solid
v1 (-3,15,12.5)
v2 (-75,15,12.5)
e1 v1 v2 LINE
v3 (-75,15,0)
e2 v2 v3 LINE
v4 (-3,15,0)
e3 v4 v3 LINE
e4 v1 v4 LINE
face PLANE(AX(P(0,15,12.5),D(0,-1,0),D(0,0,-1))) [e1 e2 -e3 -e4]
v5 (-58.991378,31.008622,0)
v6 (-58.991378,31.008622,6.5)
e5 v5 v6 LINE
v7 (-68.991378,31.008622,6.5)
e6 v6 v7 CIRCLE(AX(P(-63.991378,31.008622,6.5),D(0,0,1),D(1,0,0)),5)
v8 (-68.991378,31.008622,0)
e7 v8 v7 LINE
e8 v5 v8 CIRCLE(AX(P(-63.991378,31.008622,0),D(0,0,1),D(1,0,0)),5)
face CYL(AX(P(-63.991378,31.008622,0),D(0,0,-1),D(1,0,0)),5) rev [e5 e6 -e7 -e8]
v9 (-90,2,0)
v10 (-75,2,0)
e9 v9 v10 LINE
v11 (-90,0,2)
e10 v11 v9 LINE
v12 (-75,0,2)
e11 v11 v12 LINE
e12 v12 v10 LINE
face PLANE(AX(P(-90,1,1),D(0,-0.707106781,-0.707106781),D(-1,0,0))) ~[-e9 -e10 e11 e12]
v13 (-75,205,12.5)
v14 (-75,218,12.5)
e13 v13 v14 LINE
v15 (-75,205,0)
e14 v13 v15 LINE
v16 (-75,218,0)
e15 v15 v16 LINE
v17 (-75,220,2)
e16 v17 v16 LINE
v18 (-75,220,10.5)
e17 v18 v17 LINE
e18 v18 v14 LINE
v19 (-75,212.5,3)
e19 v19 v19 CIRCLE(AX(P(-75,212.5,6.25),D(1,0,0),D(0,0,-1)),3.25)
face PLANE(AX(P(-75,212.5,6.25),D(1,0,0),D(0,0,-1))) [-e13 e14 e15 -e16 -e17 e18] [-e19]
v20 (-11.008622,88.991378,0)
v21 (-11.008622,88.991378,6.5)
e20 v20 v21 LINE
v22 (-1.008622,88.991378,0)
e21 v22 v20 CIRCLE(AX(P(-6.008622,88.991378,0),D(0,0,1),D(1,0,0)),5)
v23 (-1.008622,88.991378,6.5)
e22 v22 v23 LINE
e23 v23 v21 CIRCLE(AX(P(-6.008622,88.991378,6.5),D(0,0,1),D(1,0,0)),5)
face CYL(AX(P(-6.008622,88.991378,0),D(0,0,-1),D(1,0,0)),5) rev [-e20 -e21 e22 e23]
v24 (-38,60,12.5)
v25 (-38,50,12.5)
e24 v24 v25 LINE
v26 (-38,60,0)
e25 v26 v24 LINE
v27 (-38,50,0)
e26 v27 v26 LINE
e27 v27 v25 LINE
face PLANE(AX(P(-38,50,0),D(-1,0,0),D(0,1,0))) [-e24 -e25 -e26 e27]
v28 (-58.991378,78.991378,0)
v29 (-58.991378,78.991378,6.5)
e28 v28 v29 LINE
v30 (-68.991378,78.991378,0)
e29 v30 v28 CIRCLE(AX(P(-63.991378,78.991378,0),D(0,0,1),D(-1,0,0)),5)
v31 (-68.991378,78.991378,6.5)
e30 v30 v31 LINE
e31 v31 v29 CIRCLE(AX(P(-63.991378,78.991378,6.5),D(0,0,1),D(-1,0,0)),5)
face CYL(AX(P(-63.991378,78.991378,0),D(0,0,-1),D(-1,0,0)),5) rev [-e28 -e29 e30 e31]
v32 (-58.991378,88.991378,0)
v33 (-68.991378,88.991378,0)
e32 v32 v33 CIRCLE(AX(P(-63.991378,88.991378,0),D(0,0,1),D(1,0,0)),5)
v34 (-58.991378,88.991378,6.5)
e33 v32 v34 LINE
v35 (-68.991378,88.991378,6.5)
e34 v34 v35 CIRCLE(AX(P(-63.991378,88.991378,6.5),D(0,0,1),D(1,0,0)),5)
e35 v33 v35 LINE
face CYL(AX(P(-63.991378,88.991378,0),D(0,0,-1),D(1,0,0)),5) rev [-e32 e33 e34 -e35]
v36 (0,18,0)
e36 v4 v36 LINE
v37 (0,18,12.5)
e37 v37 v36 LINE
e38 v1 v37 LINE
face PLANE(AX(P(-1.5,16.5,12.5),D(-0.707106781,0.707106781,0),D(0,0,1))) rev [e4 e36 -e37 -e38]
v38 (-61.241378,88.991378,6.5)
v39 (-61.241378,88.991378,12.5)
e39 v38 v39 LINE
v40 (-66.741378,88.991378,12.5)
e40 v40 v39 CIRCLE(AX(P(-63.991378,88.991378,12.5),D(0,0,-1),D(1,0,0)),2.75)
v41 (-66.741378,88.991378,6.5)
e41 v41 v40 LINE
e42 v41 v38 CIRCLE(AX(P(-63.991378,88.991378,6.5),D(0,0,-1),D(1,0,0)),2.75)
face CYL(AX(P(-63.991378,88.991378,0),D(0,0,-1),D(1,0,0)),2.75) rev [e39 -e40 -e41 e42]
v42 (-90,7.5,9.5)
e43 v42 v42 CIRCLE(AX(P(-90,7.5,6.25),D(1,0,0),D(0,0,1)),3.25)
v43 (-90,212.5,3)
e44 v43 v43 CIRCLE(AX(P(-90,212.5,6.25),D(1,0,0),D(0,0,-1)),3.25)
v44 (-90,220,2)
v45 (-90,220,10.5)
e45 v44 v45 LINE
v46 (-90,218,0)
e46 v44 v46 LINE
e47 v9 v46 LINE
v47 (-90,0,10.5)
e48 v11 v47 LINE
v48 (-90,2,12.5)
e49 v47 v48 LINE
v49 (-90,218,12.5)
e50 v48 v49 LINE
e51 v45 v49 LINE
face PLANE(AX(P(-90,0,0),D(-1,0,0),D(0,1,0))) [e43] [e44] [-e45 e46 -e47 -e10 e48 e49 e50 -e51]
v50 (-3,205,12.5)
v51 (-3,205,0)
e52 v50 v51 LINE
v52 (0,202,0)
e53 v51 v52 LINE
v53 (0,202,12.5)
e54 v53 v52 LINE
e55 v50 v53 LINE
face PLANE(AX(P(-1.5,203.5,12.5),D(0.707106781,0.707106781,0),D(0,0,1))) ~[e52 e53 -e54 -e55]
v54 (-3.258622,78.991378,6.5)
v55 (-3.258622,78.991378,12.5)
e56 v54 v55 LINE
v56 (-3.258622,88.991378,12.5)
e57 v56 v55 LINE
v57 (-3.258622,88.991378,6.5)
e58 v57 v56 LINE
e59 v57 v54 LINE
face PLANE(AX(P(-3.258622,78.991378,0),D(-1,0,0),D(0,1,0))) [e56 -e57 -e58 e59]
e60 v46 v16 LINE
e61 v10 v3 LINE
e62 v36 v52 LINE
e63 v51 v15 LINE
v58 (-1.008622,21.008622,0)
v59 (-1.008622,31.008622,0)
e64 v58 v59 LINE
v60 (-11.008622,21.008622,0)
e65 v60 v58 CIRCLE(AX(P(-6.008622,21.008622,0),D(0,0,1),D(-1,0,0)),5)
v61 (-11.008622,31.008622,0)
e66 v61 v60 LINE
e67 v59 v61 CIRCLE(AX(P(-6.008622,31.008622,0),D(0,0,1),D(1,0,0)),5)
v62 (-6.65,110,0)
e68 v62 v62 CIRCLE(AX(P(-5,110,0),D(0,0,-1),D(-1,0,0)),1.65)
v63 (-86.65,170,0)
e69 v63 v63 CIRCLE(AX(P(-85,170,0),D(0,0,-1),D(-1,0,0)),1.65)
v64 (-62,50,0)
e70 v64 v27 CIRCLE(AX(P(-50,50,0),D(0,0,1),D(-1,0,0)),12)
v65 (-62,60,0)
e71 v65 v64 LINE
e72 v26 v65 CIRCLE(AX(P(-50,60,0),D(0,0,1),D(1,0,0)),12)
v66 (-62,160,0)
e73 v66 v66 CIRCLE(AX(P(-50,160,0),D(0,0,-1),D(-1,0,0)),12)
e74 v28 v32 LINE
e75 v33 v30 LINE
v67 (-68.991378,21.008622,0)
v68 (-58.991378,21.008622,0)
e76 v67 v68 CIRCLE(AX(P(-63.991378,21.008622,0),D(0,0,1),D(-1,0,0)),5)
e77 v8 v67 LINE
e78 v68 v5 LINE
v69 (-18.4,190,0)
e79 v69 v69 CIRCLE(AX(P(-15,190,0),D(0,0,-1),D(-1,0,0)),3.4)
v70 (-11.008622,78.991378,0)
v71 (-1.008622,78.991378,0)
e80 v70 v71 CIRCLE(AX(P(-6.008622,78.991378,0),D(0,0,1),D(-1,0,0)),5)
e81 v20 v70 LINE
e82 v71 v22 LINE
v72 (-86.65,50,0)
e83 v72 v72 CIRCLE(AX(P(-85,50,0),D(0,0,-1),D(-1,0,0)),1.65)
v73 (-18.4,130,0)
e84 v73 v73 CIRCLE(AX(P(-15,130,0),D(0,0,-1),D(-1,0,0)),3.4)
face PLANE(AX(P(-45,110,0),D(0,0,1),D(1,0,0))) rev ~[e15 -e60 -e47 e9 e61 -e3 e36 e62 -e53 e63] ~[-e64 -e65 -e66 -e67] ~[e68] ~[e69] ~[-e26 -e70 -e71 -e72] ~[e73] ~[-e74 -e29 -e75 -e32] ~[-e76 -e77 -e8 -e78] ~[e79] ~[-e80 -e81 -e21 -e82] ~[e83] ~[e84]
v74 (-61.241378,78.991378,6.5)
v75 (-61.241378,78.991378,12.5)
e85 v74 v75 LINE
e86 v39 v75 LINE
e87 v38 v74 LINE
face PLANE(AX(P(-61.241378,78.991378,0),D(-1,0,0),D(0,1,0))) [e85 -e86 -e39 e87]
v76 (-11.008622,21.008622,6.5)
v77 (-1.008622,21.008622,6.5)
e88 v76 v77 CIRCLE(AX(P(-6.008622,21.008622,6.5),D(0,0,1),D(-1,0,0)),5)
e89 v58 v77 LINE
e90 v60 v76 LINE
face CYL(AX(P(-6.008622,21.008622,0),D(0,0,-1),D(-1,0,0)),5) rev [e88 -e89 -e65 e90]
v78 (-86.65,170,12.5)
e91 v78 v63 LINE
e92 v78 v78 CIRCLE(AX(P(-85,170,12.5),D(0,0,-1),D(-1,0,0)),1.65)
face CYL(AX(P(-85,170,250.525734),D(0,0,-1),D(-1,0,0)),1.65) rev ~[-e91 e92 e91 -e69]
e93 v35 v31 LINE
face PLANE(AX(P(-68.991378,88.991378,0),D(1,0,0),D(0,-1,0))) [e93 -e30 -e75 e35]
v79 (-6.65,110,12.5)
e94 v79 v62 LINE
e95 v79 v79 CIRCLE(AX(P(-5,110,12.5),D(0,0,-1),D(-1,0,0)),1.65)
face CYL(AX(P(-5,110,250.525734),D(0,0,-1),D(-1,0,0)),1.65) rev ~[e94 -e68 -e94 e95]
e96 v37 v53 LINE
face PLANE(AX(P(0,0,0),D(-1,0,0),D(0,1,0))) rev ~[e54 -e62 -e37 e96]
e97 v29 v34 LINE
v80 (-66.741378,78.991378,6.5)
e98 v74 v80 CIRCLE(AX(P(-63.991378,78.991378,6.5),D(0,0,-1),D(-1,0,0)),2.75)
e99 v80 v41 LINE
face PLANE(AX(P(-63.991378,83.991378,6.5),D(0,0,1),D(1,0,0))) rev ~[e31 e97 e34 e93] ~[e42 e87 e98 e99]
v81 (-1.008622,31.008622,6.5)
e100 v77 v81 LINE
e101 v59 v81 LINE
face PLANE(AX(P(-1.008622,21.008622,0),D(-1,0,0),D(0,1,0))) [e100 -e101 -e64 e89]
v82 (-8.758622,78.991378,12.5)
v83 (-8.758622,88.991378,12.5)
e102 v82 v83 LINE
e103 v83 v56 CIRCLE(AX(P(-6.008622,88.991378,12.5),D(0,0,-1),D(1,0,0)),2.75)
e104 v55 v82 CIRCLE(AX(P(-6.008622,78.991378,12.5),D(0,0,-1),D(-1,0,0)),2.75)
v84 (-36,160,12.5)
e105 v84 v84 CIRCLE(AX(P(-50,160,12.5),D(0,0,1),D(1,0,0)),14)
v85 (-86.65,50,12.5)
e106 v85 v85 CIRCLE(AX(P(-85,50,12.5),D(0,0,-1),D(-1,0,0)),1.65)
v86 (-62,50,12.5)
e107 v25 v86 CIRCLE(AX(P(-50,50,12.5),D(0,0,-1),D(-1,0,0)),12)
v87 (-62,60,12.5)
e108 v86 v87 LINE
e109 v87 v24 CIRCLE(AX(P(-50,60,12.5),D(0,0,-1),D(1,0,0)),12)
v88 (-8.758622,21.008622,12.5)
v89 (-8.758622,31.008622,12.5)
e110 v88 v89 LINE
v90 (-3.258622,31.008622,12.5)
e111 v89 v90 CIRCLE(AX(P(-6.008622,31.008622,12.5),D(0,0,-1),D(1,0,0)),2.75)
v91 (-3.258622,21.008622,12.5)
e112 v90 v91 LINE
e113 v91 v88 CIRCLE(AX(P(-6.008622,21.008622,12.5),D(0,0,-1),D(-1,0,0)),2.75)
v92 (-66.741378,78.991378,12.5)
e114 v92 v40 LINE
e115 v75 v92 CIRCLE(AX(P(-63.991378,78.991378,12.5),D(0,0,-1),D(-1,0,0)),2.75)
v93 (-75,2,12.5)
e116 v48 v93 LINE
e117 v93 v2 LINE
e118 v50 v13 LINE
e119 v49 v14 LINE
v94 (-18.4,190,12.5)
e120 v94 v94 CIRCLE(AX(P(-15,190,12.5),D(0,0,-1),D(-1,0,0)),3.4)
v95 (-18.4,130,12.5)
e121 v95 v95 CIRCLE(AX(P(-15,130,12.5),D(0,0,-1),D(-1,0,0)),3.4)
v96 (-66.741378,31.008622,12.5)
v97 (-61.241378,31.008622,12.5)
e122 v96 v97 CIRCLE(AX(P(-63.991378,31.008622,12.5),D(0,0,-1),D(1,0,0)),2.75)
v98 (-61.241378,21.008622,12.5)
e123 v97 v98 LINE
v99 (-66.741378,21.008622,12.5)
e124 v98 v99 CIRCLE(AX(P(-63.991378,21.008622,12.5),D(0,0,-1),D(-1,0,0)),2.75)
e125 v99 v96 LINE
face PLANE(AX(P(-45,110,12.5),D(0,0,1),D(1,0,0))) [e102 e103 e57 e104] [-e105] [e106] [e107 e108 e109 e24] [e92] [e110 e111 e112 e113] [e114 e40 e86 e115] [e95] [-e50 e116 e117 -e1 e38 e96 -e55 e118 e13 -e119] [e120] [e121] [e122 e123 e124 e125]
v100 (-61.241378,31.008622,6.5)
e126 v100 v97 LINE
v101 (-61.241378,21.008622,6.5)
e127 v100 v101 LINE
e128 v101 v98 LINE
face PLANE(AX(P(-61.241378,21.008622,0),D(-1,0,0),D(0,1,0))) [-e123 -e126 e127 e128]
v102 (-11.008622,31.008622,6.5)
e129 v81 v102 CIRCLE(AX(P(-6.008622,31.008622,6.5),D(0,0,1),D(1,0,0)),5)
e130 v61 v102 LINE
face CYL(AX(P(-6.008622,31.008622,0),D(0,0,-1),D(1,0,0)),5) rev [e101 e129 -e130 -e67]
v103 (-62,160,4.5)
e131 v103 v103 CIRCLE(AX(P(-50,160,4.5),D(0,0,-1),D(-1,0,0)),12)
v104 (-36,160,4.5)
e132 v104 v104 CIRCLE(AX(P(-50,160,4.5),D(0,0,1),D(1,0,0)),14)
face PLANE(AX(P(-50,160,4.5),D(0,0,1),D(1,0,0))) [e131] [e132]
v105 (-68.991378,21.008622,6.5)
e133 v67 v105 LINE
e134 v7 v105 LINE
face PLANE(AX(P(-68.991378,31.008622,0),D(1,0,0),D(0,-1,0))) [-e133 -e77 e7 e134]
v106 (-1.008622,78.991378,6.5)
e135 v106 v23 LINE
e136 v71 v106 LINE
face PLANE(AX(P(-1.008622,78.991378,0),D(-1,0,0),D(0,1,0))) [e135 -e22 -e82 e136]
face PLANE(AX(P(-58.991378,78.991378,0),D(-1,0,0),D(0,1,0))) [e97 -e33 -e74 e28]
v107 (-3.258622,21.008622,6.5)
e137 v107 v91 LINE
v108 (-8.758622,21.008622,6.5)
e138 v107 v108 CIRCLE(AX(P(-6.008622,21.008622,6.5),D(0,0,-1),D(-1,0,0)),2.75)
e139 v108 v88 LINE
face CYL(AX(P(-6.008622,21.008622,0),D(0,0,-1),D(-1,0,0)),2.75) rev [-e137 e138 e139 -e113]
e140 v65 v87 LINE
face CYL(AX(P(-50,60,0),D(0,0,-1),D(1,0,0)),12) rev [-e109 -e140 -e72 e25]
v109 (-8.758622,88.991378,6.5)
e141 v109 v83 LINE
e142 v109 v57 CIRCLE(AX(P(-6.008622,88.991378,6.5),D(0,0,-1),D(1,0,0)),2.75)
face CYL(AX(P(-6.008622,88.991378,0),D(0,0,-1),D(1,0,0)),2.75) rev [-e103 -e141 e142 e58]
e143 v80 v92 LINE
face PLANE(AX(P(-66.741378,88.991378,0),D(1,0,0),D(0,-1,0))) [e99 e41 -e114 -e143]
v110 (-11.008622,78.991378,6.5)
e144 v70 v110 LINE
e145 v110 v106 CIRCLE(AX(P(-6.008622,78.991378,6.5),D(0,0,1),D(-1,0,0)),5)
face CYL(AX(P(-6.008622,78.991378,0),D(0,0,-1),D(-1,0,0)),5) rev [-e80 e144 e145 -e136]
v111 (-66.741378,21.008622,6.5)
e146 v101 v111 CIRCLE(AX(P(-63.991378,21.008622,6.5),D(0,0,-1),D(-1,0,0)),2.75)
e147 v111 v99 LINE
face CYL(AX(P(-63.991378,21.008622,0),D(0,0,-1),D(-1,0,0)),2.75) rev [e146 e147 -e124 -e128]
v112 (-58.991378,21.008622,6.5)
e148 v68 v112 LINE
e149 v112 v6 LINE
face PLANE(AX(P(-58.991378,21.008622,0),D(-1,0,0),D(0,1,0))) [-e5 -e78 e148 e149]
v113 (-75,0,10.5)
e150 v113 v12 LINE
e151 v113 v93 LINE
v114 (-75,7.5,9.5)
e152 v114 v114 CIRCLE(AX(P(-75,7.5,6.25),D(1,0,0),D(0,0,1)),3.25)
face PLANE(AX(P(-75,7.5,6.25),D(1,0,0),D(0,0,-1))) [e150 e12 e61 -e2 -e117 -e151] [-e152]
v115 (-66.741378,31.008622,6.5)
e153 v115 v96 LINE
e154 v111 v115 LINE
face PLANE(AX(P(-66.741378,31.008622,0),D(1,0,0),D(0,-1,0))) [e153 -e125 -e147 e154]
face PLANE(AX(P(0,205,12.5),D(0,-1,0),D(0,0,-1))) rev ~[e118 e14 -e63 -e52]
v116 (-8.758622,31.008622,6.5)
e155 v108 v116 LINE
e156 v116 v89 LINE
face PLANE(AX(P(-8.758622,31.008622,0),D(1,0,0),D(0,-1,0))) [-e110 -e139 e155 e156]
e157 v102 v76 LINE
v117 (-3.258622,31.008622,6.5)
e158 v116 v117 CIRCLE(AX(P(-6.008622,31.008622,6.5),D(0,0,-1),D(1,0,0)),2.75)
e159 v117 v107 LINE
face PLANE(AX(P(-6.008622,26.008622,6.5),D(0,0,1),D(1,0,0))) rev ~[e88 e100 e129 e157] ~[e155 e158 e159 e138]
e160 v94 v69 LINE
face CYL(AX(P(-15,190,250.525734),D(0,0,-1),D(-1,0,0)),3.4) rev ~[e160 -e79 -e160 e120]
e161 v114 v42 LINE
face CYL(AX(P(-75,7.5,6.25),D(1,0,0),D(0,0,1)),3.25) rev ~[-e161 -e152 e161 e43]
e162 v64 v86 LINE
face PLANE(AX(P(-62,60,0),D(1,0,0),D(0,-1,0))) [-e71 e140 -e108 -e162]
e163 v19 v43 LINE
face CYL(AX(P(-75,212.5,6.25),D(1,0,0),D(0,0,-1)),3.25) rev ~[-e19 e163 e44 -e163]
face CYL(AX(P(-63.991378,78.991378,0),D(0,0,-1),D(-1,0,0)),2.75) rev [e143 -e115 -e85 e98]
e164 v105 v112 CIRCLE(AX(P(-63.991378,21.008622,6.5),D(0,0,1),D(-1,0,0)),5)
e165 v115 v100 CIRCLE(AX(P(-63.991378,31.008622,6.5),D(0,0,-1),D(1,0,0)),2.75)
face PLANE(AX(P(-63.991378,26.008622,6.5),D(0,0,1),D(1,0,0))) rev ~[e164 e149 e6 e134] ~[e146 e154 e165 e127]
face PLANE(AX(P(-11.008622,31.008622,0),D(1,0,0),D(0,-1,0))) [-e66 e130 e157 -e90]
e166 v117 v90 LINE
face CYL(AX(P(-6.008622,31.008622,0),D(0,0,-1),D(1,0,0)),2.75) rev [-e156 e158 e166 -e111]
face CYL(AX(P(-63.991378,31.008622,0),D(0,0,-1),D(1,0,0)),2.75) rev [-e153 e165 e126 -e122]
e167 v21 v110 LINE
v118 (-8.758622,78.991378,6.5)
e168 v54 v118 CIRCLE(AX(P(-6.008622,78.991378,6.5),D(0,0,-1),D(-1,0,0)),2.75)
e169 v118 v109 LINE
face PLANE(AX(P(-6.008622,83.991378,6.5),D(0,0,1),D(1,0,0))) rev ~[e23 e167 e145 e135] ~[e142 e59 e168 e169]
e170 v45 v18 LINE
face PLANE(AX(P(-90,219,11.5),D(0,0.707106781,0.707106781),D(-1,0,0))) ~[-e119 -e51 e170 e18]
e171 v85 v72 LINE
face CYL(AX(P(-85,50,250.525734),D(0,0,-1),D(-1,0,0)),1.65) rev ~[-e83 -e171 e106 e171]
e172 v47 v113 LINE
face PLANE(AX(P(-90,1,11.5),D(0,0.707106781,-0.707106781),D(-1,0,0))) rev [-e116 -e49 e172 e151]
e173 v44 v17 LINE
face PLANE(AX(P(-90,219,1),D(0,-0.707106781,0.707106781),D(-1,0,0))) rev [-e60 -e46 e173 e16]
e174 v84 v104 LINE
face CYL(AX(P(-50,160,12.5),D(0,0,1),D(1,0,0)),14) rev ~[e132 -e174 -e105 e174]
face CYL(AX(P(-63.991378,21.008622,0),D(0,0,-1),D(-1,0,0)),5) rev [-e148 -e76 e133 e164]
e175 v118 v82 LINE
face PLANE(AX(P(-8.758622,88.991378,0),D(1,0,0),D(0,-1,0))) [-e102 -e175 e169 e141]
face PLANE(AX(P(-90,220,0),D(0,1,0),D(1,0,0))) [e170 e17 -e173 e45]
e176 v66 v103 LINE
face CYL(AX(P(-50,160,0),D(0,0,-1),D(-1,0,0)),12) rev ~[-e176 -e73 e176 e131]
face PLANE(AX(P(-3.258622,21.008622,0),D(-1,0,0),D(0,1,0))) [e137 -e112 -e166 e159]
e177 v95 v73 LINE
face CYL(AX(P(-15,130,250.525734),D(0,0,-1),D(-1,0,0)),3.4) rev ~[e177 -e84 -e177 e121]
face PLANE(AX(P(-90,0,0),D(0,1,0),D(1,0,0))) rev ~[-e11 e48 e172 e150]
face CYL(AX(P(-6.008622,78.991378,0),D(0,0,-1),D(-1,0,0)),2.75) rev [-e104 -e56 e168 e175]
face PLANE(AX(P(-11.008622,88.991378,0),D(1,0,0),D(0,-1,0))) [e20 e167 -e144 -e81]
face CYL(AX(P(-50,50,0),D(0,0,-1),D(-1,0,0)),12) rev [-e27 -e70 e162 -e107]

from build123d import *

# Parameters (mm, degrees)
SKETCH_1_W               = 90
SKETCH_1_H               = 220
EXTRUDE_1_DEPTH          = 12.5
SKETCH_2_R               = 12
CUT_EXTRUDE_1_DEPTH      = 239.025733903
HOLE_WIZARD_1_AT_2_COUNT = 2
HOLE_WIZARD_1_AT_2_PITCH = 57.982756057
HOLE_WIZARD_1_AT_3_COUNT = 2
HOLE_WIZARD_1_AT_3_PITCH = 82
HOLE_WIZARD_1_AT_4_COUNT = 2
HOLE_WIZARD_1_AT_4_PITCH = 57.982756057
HOLE_WIZARD_M4_1_D       = 3.3
CUT_EXTRUDE_5_DEPTH      = 239.025733903
CUT_EXTRUDE_6_DEPTH      = 6.5
SKETCH_14_R              = 12
CUT_EXTRUDE_7_DEPTH      = 239.025733903
SKETCH_15_R              = 14
CUT_EXTRUDE_8_DEPTH      = 8
HOLE_WIZARD_M8_1_D       = 6.8
SKETCH_19_W              = 12.5
SKETCH_19_H              = 15
CUT_EXTRUDE_10_DEPTH     = 75
CHAMFER_1_SIZE           = 2
CHAMFER_2_SIZE           = 3
SKETCH_20_R              = 3.25
CUT_EXTRUDE_11_DEPTH     = 233.76866198


with BuildPart() as part:
    # 草图1 → 凸台-拉伸1 (new body)
    with BuildSketch(Plane.XY):
        with Locations((-45, 110)):
            Rectangle(SKETCH_1_W, SKETCH_1_H)
    extrude(amount=EXTRUDE_1_DEPTH)

    # 草图2 → 切除-拉伸1 (cut, through all)
    with BuildSketch(Plane.XY.offset(12.5)):
        with Locations((-50, 55)):
            Circle(SKETCH_2_R)
    extrude(amount=-CUT_EXTRUDE_1_DEPTH, mode=Mode.SUBTRACT)

    # 草图3 → 打孔尺寸根据内六角圆柱头螺钉的类型1 (revolve, cut)
    with BuildSketch(Plane(origin=(-6.008621971, 83.991378029, 12.5), x_dir=(0, -1, 0), z_dir=(1, 0, 0))):
        Polygon((0, 0), (0, 12.5), (5, 12.5), (5, 6), (2.75, 6), (2.75, 0), align=None)
    hole_wizard_1 = revolve(axis=Axis((-6.008621971, 83.991378029, 18.85), (0, 0, -1)), mode=Mode.SUBTRACT)

    # 打孔尺寸根据内六角圆柱头螺钉的类型1 at 2: 打孔尺寸根据内六角圆柱头螺钉的类型1 ×2
    with Locations(*[(0, -i * HOLE_WIZARD_1_AT_2_PITCH, 0) for i in range(1, HOLE_WIZARD_1_AT_2_COUNT)]):
        add(hole_wizard_1, mode=Mode.SUBTRACT)

    # 打孔尺寸根据内六角圆柱头螺钉的类型1 at 3: 打孔尺寸根据内六角圆柱头螺钉的类型1 ×2
    with Locations(*[Vector(-0.7071067811865412, -0.7071067811865539, 0) * (i * HOLE_WIZARD_1_AT_3_PITCH) for i in range(1, HOLE_WIZARD_1_AT_3_COUNT)]):
        add(hole_wizard_1, mode=Mode.SUBTRACT)

    # 打孔尺寸根据内六角圆柱头螺钉的类型1 at 4: 打孔尺寸根据内六角圆柱头螺钉的类型1 ×2
    with Locations(*[(-i * HOLE_WIZARD_1_AT_4_PITCH, 0, 0) for i in range(1, HOLE_WIZARD_1_AT_4_COUNT)]):
        add(hole_wizard_1, mode=Mode.SUBTRACT)

    # M4 螺纹孔1 (through all)
    with Locations(Plane.XY.offset(12.5)):
        with Locations((-85, 170), (-85, 50), (-5, 110)):
            Hole(HOLE_WIZARD_M4_1_D / 2)

    # 草图12 → 切除-拉伸5 (cut, through all)
    with BuildSketch(Plane(origin=(0, 0, 0), x_dir=(-1, 0, 0), z_dir=(0, 0, -1))):
        with BuildLine():
            Line((38, 50), (38, 60))
            ThreePointArc((38, 60), (50, 72), (62, 60))
            Line((62, 60), (62, 50))
            ThreePointArc((62, 50), (50, 38), (38, 50))
        make_face()
        with BuildLine():
            Line((61.241378029, 78.991378029), (61.241378029, 88.991378029))
            ThreePointArc((61.241378029, 88.991378029), (63.991378029, 91.741378029), (66.741378029, 88.991378029))
            Line((66.741378029, 88.991378029), (66.741378029, 78.991378029))
            ThreePointArc((66.741378029, 78.991378029), (63.991378029, 76.241378029), (61.241378029, 78.991378029))
        make_face()
        with BuildLine():
            Line((66.741378029, 31.008621971), (66.741378029, 21.008621971))
            ThreePointArc((66.741378029, 21.008621971), (63.991378029, 18.258621971), (61.241378029, 21.008621971))
            Line((61.241378029, 21.008621971), (61.241378029, 31.008621971))
            ThreePointArc((61.241378029, 31.008621971), (63.991378029, 33.758621971), (66.741378029, 31.008621971))
        make_face()
        with BuildLine():
            Line((8.758621971, 31.008621971), (8.758621971, 21.008621971))
            ThreePointArc((8.758621971, 21.008621971), (6.008621971, 18.258621971), (3.258621971, 21.008621971))
            Line((3.258621971, 21.008621971), (3.258621971, 31.008621971))
            ThreePointArc((3.258621971, 31.008621971), (6.008621971, 33.758621971), (8.758621971, 31.008621971))
        make_face()
        with BuildLine():
            Line((8.758621971, 88.991378029), (8.758621971, 78.991378029))
            ThreePointArc((8.758621971, 78.991378029), (6.008621971, 76.241378029), (3.258621971, 78.991378029))
            Line((3.258621971, 78.991378029), (3.258621971, 88.991378029))
            ThreePointArc((3.258621971, 88.991378029), (6.008621971, 91.741378029), (8.758621971, 88.991378029))
        make_face()
    extrude(amount=-CUT_EXTRUDE_5_DEPTH, mode=Mode.SUBTRACT)

    # 草图13 → 切除-拉伸6 (cut)
    with BuildSketch(Plane(origin=(0, 0, 0), x_dir=(-1, 0, 0), z_dir=(0, 0, -1))):
        with BuildLine():
            Line((11.008621971, 88.991378029), (11.008621971, 78.991378029))
            ThreePointArc((11.008621971, 78.991378029), (6.008621971, 73.991378029), (1.008621971, 78.991378029))
            Line((1.008621971, 78.991378029), (1.008621971, 88.991378029))
            ThreePointArc((1.008621971, 88.991378029), (6.008621971, 93.991378029), (11.008621971, 88.991378029))
        make_face()
        with BuildLine():
            Line((68.991378029, 88.991378029), (68.991378029, 78.991378029))
            ThreePointArc((68.991378029, 78.991378029), (63.991378029, 73.991378029), (58.991378029, 78.991378029))
            Line((58.991378029, 78.991378029), (58.991378029, 88.991378029))
            ThreePointArc((58.991378029, 88.991378029), (63.991378029, 93.991378029), (68.991378029, 88.991378029))
        make_face()
        with BuildLine():
            Line((11.008621971, 31.008621971), (11.008621971, 21.008621971))
            ThreePointArc((11.008621971, 21.008621971), (6.008621971, 16.008621971), (1.008621971, 21.008621971))
            Line((1.008621971, 21.008621971), (1.008621971, 31.008621971))
            ThreePointArc((1.008621971, 31.008621971), (6.008621971, 36.008621971), (11.008621971, 31.008621971))
        make_face()
        with BuildLine():
            Line((68.991378029, 31.008621971), (68.991378029, 21.008621971))
            ThreePointArc((68.991378029, 21.008621971), (63.991378029, 16.008621971), (58.991378029, 21.008621971))
            Line((58.991378029, 21.008621971), (58.991378029, 31.008621971))
            ThreePointArc((58.991378029, 31.008621971), (63.991378029, 36.008621971), (68.991378029, 31.008621971))
        make_face()
    extrude(amount=-CUT_EXTRUDE_6_DEPTH, mode=Mode.SUBTRACT)

    # 草图14 → 切除-拉伸7 (cut, through all)
    with BuildSketch(Plane(origin=(0, 0, 0), x_dir=(-1, 0, 0), z_dir=(0, 0, -1))):
        with Locations((50, 160)):
            Circle(SKETCH_14_R)
    extrude(amount=-CUT_EXTRUDE_7_DEPTH, mode=Mode.SUBTRACT)

    # 草图15 → 切除-拉伸8 (cut)
    with BuildSketch(Plane.XY.offset(12.5)):
        with Locations((-50, 160)):
            Circle(SKETCH_15_R)
    extrude(amount=-CUT_EXTRUDE_8_DEPTH, mode=Mode.SUBTRACT)

    # M8 螺纹孔1 (through all)
    with Locations(Plane.XY.offset(12.5)):
        with Locations((-15, 130), (-15, 190)):
            Hole(HOLE_WIZARD_M8_1_D / 2)

    # 草图19 → 切除-拉伸10 (cut)
    with BuildSketch(Plane(origin=(0, 0, 0), x_dir=(0, 0, -1), z_dir=(1, 0, 0))):
        with Locations((-6.25, 212.5)):
            Rectangle(SKETCH_19_W, SKETCH_19_H)
        with Locations((-6.25, 7.5)):
            Rectangle(SKETCH_19_W, SKETCH_19_H)
    extrude(amount=-CUT_EXTRUDE_10_DEPTH, mode=Mode.SUBTRACT)

    # 倒角1
    chamfer_1_edges = [part.edges().sort_by_distance(p)[0] for p in [
        (-82.5, 220, 0),
        (-82.5, 220, 12.5),
        (-82.5, 0, 0),
        (-82.5, 0, 12.5),
    ]]
    chamfer(chamfer_1_edges, length=CHAMFER_1_SIZE)

    # 倒角2
    chamfer_2_edges = [part.edges().sort_by_distance(p)[0] for p in [
        (0, 205, 6.25),
        (0, 15, 6.25),
    ]]
    chamfer(chamfer_2_edges, length=CHAMFER_2_SIZE)

    # 草图20 → 切除-拉伸11 (cut, through all)
    with BuildSketch(Plane(origin=(-75, 0, 0), x_dir=(0, 0, -1), z_dir=(1, 0, 0))):
        with Locations((-6.25, 212.5)):
            Circle(SKETCH_20_R)
        with Locations(Location((-6.25, 7.5, 0), (0, 0, 180))):
            Circle(SKETCH_20_R)
    extrude(amount=-CUT_EXTRUDE_11_DEPTH, mode=Mode.SUBTRACT)


solid = part.part
